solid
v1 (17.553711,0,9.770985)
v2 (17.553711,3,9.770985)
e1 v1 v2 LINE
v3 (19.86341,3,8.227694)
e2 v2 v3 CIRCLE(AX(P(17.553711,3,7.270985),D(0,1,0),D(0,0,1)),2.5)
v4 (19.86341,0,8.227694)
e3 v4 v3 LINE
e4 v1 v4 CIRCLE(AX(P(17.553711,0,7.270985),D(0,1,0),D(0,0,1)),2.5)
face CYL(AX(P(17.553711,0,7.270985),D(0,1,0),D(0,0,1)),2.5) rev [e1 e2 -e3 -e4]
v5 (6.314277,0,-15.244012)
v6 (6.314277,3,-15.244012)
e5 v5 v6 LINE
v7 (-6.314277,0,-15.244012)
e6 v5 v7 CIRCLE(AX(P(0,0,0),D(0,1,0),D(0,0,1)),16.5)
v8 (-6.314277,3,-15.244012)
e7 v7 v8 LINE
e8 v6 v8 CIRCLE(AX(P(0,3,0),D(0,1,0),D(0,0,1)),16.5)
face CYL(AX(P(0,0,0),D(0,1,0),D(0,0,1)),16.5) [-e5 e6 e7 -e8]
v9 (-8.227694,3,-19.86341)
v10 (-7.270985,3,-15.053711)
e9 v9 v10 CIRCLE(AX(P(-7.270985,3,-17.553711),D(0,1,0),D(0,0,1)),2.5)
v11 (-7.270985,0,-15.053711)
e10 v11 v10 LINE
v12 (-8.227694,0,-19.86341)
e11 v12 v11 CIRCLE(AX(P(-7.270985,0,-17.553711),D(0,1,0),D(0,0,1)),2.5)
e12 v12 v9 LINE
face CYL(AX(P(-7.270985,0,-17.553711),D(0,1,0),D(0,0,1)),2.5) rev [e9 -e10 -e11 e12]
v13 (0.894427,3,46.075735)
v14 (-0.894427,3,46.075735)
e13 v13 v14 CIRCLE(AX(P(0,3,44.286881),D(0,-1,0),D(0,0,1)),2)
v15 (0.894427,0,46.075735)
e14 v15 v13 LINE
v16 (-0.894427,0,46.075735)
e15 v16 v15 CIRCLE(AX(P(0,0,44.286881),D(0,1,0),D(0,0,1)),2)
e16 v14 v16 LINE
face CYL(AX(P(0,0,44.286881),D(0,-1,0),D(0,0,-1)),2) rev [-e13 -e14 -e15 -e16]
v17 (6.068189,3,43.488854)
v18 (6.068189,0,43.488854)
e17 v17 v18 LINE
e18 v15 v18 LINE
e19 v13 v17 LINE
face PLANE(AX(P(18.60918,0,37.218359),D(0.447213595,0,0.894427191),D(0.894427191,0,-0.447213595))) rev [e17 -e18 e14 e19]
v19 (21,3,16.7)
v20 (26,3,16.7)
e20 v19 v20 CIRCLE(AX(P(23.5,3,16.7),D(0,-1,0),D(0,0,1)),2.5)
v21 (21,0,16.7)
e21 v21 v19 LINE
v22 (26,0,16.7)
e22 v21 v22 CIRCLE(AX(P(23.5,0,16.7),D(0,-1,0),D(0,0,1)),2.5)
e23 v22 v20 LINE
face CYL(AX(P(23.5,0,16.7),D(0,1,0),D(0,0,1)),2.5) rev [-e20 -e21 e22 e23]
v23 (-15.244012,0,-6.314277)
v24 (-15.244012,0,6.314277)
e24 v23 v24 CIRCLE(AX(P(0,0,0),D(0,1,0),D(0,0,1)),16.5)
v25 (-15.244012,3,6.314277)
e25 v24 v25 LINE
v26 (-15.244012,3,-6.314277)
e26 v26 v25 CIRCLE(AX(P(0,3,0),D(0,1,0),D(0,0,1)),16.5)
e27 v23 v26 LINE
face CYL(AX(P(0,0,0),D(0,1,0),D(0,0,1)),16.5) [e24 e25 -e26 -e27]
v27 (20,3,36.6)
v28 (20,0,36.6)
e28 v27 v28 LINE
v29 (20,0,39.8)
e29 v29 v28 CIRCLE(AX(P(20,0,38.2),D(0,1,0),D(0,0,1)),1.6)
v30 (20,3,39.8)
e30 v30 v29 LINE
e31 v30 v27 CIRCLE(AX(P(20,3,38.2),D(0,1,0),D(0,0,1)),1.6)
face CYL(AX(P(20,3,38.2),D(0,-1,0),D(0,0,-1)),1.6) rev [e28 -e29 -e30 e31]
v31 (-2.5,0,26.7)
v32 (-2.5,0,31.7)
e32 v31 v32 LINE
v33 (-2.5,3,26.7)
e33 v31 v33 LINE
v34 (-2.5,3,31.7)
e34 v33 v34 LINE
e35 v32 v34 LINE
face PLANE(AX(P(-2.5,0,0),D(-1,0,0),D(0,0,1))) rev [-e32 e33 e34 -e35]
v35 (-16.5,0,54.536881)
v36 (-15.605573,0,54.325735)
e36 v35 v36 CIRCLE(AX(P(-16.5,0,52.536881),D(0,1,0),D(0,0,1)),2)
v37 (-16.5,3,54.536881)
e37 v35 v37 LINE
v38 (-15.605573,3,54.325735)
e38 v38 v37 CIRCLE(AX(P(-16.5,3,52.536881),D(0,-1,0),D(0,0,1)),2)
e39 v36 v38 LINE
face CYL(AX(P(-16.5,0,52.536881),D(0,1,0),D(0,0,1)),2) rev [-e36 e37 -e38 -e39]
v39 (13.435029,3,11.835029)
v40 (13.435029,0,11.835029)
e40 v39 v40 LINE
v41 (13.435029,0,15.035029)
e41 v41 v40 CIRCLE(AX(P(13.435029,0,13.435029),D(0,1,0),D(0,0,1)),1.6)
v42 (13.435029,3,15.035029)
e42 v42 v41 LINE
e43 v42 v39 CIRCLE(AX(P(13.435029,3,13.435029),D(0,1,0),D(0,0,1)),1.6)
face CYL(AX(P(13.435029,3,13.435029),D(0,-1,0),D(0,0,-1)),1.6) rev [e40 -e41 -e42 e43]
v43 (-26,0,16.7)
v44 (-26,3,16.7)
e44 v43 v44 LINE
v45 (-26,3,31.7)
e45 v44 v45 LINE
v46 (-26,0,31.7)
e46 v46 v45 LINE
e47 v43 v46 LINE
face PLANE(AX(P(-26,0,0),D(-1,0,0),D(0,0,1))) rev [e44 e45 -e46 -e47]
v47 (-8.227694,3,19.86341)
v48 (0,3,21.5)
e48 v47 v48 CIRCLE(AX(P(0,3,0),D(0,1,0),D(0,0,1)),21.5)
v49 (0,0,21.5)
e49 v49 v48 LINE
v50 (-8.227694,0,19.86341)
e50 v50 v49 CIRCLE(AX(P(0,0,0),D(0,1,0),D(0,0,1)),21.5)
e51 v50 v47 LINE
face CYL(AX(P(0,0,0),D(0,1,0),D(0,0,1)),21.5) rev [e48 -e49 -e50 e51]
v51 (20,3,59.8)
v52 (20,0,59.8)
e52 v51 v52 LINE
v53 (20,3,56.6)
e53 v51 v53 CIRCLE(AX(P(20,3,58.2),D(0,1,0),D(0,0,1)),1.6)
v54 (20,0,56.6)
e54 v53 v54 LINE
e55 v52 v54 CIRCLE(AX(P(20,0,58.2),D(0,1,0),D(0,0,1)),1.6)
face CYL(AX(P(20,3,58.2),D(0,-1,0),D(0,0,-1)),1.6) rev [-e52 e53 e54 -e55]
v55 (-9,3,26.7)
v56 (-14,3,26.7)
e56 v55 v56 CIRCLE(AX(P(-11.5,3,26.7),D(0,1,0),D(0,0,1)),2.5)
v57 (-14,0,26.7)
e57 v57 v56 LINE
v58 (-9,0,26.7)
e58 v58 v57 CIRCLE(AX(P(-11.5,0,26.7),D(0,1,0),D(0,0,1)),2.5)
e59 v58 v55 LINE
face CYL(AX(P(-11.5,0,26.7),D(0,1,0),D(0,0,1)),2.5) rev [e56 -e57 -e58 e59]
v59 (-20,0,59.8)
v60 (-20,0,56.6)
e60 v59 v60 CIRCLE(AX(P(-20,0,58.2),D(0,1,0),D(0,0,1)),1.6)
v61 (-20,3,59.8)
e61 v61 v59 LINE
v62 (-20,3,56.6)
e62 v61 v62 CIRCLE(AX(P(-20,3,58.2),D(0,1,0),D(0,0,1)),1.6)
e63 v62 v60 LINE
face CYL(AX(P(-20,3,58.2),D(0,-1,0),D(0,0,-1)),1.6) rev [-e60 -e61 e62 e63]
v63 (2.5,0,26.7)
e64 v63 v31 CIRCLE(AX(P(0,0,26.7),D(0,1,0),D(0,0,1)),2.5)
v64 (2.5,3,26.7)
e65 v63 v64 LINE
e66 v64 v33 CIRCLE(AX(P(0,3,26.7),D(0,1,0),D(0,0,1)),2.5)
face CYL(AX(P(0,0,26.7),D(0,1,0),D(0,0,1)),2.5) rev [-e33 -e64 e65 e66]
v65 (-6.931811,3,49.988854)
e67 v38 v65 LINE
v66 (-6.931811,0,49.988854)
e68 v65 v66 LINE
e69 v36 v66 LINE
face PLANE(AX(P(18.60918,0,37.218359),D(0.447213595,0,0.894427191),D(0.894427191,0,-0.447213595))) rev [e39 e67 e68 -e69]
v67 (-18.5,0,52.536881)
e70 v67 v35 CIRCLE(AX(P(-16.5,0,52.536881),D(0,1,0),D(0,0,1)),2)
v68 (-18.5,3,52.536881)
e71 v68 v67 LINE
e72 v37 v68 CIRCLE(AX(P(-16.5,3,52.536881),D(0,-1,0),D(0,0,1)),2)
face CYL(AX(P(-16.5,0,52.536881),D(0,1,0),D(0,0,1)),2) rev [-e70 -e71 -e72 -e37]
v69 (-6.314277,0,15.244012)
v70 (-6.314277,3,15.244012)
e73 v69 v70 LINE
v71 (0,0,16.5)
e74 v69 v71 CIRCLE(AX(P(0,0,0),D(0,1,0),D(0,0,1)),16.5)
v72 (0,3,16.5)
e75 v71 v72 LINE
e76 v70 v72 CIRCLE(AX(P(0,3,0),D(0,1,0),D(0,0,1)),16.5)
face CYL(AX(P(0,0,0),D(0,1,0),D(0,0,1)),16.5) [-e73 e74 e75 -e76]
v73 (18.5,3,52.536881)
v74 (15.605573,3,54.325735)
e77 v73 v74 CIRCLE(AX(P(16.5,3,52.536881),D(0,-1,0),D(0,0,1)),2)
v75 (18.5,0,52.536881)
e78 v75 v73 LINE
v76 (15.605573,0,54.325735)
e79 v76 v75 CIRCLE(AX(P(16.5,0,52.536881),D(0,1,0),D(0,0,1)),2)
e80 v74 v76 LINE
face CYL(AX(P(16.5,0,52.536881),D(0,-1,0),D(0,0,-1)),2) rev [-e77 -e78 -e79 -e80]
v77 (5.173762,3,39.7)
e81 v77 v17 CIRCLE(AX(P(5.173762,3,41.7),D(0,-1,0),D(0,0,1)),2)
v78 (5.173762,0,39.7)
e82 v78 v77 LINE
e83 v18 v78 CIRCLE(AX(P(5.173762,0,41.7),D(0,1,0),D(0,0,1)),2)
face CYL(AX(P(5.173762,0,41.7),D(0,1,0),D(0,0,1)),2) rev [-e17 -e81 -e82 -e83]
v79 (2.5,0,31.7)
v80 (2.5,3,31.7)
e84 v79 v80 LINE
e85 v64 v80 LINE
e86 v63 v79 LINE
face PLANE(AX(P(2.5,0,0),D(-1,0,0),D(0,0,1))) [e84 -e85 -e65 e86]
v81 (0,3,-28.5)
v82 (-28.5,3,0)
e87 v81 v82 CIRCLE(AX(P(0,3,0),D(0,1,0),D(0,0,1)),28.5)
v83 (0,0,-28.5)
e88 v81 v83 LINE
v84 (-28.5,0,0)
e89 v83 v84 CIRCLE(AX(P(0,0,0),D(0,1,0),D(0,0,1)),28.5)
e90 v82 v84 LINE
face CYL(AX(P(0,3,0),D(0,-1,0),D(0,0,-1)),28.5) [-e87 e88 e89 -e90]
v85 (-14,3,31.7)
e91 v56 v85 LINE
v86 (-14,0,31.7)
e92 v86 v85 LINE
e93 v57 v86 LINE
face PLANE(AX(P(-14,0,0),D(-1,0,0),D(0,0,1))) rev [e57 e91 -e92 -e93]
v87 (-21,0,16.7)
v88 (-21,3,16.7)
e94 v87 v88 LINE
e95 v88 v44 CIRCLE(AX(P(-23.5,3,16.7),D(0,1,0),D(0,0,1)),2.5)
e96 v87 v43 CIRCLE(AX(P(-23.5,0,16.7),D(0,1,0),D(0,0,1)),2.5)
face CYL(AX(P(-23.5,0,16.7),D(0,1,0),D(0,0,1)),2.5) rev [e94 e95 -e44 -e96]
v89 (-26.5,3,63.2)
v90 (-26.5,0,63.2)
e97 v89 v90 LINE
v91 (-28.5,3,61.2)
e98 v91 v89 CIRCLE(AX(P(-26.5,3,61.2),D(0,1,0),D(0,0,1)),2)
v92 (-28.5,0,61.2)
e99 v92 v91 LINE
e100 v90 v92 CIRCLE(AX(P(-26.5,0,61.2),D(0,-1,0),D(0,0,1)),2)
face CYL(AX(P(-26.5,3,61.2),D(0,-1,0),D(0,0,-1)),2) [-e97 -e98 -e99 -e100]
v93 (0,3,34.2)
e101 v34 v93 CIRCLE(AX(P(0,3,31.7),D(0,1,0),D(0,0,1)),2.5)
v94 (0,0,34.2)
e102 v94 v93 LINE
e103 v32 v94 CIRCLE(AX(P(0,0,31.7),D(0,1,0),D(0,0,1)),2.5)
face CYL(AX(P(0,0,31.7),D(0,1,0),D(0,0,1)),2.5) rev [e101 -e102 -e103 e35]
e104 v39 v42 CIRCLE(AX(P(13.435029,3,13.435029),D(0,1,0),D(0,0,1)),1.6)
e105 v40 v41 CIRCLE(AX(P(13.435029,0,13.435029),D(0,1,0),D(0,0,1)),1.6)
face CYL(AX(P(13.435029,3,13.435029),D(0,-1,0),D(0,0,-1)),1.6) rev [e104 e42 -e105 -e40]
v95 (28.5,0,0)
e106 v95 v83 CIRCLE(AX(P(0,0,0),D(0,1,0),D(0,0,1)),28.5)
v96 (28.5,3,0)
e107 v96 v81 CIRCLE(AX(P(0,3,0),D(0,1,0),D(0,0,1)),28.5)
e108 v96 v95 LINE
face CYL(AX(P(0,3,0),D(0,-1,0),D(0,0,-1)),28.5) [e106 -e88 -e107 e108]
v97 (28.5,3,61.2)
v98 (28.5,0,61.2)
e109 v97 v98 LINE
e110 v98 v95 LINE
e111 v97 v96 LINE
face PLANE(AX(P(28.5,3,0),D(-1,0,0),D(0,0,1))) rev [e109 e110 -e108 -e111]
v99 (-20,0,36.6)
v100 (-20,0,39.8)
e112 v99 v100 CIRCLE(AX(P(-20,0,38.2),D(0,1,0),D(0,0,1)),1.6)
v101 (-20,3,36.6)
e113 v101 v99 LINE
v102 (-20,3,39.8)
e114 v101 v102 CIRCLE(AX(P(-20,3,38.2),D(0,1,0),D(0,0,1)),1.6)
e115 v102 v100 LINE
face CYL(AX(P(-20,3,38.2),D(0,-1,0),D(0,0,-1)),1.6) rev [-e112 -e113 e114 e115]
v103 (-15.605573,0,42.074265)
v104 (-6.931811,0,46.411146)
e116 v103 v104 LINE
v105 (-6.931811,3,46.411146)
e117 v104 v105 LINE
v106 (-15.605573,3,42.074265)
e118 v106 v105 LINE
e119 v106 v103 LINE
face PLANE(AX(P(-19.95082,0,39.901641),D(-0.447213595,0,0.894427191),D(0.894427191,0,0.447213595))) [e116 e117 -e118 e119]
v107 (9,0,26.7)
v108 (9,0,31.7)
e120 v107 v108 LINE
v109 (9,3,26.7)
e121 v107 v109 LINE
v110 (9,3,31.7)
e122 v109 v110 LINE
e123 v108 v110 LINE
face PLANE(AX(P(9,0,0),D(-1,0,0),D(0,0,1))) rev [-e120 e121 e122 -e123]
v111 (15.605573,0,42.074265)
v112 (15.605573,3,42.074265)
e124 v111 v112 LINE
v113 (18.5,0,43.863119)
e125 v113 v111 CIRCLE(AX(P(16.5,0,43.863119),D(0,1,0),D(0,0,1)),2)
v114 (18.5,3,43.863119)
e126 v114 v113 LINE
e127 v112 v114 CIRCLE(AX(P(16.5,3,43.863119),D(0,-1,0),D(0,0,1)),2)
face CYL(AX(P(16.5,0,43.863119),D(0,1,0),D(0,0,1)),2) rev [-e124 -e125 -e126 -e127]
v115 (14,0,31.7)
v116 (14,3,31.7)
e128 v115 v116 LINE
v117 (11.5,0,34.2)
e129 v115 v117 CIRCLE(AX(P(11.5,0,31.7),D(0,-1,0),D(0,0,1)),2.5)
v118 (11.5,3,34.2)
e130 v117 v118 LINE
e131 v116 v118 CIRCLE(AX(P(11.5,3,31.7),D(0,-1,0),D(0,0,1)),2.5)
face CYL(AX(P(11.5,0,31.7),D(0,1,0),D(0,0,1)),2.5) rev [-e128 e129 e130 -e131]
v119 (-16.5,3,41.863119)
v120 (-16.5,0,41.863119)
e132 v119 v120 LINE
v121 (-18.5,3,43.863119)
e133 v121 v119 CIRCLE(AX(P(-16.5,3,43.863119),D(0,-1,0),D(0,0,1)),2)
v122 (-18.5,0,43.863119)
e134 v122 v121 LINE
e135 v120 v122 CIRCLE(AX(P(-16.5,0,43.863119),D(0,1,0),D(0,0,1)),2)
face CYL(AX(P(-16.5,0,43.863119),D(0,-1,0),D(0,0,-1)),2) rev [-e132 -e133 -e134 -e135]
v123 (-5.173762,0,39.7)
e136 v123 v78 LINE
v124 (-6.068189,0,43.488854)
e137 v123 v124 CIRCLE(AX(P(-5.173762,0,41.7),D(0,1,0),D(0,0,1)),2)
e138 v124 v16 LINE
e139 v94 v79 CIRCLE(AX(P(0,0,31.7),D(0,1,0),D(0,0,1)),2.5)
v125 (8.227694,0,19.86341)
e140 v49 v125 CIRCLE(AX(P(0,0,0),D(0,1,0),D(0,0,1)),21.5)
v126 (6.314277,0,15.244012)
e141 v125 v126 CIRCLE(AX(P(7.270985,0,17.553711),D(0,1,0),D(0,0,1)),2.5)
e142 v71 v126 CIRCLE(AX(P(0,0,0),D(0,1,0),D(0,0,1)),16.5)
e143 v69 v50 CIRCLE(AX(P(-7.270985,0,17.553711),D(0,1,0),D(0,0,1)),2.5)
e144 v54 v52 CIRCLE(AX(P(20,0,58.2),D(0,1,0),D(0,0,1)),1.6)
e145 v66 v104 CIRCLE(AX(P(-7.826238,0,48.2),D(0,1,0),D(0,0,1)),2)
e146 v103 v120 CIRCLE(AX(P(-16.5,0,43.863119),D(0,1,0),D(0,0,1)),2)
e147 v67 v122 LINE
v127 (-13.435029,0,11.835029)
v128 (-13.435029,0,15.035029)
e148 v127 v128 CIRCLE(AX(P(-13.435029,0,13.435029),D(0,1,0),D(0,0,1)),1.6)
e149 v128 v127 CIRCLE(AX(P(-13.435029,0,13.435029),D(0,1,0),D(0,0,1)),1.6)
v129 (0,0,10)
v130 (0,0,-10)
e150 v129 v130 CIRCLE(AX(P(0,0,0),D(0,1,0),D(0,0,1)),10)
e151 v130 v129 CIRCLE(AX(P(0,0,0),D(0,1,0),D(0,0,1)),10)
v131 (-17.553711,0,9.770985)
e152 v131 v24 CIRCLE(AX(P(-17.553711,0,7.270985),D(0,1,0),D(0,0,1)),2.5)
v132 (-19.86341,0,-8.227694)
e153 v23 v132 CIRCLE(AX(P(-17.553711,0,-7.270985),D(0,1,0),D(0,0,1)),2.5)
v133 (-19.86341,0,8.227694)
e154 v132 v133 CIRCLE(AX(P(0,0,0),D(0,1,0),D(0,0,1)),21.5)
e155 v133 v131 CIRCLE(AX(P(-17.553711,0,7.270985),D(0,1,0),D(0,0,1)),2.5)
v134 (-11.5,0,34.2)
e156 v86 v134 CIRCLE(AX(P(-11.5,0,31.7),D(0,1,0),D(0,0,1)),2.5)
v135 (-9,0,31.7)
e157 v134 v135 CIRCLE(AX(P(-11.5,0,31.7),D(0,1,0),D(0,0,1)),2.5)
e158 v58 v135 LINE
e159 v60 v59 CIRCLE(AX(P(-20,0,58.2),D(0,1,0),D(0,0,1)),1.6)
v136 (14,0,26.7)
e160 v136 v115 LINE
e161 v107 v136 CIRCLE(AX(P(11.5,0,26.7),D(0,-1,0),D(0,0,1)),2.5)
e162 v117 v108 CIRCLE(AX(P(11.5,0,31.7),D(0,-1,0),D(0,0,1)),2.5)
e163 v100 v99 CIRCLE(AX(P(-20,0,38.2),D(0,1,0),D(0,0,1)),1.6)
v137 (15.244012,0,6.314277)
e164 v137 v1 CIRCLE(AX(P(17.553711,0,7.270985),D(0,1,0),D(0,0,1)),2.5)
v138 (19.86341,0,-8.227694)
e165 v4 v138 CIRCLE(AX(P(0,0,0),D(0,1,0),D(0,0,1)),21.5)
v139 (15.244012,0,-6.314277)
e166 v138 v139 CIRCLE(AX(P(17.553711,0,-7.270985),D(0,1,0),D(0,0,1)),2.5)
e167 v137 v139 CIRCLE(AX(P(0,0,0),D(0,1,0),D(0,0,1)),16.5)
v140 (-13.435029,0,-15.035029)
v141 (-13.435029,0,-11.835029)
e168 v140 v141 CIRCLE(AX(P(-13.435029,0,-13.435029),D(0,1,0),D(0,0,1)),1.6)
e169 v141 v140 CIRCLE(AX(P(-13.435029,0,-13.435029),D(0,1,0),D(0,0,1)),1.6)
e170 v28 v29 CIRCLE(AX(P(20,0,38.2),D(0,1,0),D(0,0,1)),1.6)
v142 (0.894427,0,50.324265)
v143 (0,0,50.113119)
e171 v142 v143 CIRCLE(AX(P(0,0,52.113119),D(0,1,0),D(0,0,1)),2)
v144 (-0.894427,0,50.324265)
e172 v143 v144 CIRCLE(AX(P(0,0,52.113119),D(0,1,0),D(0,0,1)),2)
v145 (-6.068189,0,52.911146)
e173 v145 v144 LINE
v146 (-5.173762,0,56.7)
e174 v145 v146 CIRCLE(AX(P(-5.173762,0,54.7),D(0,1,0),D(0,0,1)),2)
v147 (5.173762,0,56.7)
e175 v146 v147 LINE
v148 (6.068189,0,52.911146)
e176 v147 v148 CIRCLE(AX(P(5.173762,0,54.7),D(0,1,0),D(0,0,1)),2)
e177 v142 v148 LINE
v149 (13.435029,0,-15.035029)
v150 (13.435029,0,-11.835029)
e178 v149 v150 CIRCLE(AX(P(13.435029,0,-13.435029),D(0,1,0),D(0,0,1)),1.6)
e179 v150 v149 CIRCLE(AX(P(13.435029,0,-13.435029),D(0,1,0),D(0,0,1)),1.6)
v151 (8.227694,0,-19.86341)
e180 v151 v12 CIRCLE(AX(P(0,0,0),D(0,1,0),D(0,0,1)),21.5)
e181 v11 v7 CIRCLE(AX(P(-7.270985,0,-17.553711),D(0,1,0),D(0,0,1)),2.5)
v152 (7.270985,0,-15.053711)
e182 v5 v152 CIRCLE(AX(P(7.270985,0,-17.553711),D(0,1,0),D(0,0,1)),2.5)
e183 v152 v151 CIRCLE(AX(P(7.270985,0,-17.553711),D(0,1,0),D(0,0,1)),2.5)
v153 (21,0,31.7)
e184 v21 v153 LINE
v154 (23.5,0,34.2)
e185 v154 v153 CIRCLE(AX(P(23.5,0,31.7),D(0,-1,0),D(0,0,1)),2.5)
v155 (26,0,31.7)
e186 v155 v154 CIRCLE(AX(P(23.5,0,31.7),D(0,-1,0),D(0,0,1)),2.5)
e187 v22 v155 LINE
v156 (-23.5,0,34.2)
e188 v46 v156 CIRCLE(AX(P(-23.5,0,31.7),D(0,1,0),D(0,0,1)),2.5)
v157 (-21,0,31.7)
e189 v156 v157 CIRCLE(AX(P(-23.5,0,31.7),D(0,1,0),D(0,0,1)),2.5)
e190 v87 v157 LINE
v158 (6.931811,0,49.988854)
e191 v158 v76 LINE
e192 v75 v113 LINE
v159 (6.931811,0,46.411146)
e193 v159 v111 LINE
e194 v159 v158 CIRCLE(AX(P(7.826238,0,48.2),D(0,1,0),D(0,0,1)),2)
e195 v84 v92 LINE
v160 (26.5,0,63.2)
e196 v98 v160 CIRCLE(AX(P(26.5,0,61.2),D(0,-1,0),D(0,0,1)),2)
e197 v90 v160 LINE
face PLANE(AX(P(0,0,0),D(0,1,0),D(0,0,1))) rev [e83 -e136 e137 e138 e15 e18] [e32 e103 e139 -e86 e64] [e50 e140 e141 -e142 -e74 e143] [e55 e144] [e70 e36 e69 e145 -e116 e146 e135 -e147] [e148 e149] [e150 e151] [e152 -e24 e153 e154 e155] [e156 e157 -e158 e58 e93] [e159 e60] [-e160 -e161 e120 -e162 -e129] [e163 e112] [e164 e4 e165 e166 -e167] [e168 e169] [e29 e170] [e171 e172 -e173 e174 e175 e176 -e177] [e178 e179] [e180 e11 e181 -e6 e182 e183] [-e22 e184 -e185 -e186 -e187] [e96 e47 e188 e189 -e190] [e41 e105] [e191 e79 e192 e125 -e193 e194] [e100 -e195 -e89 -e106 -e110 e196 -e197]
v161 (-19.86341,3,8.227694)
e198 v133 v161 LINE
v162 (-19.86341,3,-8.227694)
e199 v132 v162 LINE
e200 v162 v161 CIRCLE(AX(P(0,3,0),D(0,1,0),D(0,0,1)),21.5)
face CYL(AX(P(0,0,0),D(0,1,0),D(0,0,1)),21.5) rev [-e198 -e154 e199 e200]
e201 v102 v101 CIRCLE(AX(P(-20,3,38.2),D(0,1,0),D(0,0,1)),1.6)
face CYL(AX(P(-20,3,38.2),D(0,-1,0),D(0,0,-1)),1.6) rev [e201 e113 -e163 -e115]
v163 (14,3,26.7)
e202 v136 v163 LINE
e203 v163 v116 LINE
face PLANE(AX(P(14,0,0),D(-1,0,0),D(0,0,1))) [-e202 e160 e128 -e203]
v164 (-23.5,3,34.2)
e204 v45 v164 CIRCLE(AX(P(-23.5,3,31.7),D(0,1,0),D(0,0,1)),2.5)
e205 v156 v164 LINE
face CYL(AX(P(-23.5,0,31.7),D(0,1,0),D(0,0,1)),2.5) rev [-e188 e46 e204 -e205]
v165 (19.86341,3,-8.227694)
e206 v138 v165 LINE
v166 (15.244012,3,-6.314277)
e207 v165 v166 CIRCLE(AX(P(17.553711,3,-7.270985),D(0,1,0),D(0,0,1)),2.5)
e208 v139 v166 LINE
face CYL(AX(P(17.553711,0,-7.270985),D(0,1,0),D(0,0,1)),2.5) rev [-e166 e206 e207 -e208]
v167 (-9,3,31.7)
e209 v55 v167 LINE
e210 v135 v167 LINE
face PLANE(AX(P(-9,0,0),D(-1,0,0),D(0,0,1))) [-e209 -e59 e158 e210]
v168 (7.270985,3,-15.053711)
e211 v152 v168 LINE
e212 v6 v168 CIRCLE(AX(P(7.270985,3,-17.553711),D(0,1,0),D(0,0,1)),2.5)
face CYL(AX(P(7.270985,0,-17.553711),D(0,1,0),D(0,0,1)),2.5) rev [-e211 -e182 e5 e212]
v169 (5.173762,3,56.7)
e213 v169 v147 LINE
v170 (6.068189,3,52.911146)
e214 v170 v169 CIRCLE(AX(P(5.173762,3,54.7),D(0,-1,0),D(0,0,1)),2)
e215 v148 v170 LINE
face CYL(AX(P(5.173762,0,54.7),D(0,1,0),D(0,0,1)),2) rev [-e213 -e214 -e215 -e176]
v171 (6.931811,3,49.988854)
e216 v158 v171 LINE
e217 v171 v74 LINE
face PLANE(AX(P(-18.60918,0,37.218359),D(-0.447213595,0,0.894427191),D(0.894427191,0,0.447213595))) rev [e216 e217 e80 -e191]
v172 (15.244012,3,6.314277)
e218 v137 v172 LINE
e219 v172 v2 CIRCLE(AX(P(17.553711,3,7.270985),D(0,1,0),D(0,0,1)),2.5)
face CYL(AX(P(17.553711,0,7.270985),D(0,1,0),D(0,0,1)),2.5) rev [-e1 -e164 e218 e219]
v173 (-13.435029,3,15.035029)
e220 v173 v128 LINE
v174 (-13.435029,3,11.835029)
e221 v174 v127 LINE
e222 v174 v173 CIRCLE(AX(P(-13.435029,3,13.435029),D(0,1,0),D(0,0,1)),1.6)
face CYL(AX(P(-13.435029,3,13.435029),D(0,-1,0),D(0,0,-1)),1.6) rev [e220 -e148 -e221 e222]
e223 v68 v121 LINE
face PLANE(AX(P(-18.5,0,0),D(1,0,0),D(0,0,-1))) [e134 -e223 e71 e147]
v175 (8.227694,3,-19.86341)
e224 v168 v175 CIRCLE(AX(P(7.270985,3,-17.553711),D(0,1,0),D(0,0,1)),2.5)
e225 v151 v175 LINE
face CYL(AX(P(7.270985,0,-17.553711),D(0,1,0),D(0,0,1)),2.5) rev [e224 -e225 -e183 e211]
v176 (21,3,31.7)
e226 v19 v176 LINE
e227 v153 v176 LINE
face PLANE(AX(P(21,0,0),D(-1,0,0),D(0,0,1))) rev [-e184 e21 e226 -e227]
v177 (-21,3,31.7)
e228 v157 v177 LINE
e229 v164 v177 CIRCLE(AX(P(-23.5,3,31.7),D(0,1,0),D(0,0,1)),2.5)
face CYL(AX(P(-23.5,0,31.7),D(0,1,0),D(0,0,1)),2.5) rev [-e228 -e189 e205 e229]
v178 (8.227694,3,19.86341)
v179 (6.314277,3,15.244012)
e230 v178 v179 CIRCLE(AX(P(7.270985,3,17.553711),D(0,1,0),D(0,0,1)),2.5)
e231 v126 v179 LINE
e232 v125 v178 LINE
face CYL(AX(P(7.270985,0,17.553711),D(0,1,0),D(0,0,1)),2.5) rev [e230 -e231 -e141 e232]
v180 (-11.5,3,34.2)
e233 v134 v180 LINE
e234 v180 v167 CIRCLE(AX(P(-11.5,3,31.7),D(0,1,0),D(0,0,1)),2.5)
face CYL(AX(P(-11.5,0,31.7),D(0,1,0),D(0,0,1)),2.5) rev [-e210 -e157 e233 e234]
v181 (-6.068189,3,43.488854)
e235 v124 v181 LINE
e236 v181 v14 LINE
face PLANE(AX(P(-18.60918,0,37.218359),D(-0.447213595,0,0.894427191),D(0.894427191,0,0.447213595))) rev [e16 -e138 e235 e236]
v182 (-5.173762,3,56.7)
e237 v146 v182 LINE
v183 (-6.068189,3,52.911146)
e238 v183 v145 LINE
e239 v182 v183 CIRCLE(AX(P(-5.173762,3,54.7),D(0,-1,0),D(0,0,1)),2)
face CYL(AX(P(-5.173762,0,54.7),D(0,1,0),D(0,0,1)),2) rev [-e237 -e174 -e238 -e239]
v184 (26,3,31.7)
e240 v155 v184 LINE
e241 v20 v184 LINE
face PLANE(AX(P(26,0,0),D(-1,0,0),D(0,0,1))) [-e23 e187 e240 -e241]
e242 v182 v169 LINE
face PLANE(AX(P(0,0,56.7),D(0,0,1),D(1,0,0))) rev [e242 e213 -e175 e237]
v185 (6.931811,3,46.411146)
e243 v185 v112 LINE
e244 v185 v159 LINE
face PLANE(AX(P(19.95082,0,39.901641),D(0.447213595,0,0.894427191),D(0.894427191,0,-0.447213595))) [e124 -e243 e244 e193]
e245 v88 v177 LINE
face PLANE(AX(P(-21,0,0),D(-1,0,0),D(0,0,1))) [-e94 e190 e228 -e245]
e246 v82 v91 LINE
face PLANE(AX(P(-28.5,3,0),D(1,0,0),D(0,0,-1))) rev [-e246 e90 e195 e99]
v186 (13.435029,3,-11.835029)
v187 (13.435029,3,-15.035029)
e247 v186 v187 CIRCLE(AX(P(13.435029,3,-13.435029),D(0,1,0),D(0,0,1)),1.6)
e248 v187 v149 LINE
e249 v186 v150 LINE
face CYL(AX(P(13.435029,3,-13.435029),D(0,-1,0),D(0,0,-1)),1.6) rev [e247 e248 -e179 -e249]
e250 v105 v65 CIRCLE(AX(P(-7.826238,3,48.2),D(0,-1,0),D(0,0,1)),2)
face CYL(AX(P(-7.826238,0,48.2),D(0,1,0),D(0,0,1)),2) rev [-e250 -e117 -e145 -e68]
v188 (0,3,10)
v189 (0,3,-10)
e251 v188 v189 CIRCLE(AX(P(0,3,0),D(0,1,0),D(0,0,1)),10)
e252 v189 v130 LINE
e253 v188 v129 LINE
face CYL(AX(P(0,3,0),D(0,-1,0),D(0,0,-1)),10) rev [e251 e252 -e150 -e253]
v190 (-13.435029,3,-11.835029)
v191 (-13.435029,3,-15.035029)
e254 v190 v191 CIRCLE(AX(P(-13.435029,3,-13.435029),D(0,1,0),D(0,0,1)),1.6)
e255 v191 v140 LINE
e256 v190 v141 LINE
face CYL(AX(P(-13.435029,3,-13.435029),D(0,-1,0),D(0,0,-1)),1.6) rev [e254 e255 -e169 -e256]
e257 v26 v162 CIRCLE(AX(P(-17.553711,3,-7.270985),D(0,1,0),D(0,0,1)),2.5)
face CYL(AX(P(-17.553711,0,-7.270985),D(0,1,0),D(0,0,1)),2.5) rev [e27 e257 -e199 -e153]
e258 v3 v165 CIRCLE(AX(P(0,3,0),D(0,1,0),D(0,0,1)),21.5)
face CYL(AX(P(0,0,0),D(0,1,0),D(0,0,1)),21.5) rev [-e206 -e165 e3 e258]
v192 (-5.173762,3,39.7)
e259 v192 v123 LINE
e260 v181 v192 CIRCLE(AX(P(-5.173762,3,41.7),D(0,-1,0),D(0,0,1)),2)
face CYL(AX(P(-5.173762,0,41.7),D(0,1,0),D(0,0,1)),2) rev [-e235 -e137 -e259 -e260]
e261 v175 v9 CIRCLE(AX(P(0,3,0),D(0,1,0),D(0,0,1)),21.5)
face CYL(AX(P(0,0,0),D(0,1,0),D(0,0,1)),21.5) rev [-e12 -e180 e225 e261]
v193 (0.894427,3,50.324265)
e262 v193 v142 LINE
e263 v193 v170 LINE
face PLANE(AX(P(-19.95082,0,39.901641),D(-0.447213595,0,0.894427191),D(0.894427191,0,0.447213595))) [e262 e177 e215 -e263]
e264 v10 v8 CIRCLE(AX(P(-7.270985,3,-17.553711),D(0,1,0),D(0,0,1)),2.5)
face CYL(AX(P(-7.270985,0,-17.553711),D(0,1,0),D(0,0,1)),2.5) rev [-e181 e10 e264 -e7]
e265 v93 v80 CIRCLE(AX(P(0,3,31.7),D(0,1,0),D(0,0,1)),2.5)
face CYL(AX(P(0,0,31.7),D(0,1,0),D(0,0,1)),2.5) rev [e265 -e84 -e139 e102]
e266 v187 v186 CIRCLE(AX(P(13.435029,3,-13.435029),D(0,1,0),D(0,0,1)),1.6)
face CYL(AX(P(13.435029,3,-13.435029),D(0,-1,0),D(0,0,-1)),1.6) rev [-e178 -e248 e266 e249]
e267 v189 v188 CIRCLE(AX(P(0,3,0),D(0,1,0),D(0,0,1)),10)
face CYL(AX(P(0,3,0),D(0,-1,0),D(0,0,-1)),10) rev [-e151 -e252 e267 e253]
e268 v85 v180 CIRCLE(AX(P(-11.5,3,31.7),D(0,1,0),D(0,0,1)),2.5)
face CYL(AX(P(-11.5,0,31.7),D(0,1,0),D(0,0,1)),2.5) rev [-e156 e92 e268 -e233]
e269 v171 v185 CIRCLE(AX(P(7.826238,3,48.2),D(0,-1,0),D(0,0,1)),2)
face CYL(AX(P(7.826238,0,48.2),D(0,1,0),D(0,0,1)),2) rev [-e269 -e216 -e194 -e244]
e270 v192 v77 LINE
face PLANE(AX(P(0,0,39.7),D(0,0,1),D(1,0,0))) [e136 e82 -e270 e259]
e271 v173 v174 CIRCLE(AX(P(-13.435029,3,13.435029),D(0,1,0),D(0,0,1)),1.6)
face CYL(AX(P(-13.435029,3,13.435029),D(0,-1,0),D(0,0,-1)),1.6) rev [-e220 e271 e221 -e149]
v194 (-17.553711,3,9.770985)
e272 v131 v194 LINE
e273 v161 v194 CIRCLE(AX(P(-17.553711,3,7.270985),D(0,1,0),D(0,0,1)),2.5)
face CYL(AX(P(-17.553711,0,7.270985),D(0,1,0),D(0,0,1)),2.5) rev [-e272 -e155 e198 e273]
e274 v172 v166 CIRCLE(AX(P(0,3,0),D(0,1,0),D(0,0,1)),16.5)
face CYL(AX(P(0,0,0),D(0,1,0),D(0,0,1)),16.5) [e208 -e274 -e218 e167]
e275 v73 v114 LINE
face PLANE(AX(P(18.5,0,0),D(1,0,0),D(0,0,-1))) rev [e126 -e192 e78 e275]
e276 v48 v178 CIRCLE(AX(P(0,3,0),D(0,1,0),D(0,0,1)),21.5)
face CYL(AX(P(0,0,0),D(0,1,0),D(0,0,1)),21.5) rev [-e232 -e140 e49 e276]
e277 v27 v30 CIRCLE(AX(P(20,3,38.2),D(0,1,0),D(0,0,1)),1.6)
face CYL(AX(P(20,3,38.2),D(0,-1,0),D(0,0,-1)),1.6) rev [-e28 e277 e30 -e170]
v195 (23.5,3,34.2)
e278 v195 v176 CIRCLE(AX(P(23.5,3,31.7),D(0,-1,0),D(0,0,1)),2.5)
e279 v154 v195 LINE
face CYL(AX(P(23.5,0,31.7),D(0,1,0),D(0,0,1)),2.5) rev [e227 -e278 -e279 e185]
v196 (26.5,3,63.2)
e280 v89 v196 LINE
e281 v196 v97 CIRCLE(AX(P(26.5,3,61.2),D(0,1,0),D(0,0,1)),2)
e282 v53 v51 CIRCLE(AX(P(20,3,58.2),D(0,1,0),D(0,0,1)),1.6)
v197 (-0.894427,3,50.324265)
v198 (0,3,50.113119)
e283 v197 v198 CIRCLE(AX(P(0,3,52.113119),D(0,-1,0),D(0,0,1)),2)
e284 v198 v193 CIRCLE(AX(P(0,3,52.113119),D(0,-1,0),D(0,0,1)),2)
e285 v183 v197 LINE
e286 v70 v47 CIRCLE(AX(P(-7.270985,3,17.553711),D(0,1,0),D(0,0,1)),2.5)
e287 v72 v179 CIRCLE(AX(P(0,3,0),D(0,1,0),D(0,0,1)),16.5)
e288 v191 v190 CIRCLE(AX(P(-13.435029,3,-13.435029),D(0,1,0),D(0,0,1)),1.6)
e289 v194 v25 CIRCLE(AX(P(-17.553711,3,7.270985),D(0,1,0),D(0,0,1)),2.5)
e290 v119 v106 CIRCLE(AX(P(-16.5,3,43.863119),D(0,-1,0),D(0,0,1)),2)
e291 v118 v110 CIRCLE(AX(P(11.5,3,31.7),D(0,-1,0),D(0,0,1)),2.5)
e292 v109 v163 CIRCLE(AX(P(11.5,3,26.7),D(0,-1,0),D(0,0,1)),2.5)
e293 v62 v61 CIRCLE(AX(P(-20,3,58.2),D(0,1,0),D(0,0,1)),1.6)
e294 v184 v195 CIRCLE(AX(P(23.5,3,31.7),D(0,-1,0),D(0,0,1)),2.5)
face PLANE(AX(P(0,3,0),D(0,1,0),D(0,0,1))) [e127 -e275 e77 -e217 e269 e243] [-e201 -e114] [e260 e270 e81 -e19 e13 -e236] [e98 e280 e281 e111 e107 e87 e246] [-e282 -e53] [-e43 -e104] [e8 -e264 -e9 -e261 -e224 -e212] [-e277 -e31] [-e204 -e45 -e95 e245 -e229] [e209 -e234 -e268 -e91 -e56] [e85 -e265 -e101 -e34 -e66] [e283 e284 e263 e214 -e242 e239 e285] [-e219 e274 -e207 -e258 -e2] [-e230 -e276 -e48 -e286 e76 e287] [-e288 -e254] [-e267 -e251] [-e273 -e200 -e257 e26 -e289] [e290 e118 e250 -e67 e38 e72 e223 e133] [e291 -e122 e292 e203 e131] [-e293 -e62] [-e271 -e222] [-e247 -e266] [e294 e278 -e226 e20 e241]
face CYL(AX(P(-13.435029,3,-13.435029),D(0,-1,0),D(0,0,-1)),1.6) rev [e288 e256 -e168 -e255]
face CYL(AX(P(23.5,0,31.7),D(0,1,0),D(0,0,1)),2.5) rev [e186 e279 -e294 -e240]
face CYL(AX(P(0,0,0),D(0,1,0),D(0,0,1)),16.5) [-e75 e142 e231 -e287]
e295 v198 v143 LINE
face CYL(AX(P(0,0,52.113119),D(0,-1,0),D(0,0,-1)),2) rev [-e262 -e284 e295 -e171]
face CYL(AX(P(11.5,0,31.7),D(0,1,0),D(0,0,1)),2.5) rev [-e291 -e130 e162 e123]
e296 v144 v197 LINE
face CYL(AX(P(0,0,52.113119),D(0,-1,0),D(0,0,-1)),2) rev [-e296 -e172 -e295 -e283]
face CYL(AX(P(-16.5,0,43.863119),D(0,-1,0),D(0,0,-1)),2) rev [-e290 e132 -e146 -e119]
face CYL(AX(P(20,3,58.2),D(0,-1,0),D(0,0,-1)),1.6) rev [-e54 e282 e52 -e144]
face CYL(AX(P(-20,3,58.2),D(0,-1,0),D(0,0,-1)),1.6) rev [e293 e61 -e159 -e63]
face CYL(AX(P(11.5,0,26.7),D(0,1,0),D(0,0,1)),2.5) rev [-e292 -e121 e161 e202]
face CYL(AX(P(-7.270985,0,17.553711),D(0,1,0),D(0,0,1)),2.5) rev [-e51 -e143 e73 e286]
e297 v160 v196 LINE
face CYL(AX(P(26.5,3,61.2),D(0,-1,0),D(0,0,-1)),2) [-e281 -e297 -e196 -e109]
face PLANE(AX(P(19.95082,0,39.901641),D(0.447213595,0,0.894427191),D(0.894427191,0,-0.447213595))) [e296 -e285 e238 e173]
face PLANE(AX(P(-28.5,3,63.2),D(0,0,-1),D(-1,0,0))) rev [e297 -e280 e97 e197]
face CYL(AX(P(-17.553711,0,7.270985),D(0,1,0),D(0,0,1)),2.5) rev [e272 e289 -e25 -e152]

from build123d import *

# Parameters (mm, degrees)
SKETCH_1_R          = 1.6
SKETCH_1_R_2        = 10
EXTRUDE_1_DEPTH     = 3
CUT_EXTRUDE_1_DEPTH = 3
FILLET_1_R          = 2


with BuildPart() as part:
    # 草图1 → 凸台-拉伸1 (new body)
    with BuildSketch(Plane(origin=(0, 0, 0), x_dir=(1, 0, 0), z_dir=(0, 1, 0))):
        with BuildLine():
            Line((-28.5, 0), (-28.5, -63.2))
            Line((-28.5, -63.2), (28.5, -63.2))
            Line((28.5, -63.2), (28.5, 0))
            ThreePointArc((28.5, 0), (0, 28.5), (-28.5, 0))
        make_face()
        with Locations(Location((-20, -38.2, 0), (0, 0, 270))):
            Circle(SKETCH_1_R, mode=Mode.SUBTRACT)
        with Locations(Location((20, -38.2, 0), (0, 0, 270))):
            Circle(SKETCH_1_R, mode=Mode.SUBTRACT)
        with Locations(Location((20, -58.2, 0), (0, 0, 270))):
            Circle(SKETCH_1_R, mode=Mode.SUBTRACT)
        with Locations(Location((-20, -58.2, 0), (0, 0, 270))):
            Circle(SKETCH_1_R, mode=Mode.SUBTRACT)
        with Locations(Location((0, 0, 0), (0, 0, 270))):
            Circle(SKETCH_1_R_2, mode=Mode.SUBTRACT)
        with Locations(Location((-13.435028843, 13.435028843, 0), (0, 0, 270))):
            Circle(SKETCH_1_R, mode=Mode.SUBTRACT)
        with Locations(Location((13.435028843, 13.435028843, 0), (0, 0, 270))):
            Circle(SKETCH_1_R, mode=Mode.SUBTRACT)
        with Locations(Location((13.435028843, -13.435028843, 0), (0, 0, 270))):
            Circle(SKETCH_1_R, mode=Mode.SUBTRACT)
        with Locations(Location((-13.435028843, -13.435028843, 0), (0, 0, 270))):
            Circle(SKETCH_1_R, mode=Mode.SUBTRACT)
    extrude(amount=EXTRUDE_1_DEPTH)

    # 草图2 → 切除-拉伸1 (cut)
    with BuildSketch(Plane(origin=(0, 3, 0), x_dir=(1, 0, 0), z_dir=(0, 1, 0))):
        Polygon((-18.5, -40.627050983), (-18.5, -55.772949017), (-3.354101966, -48.2), align=None)
        Polygon((13.645898034, -39.7), (-13.645898034, -39.7), (0, -46.522949017), align=None)
        Polygon((3.354101966, -48.2), (18.5, -55.772949017), (18.5, -40.627050983), align=None)
        Polygon((0, -49.877050983), (-13.645898034, -56.7), (13.645898034, -56.7), align=None)
        with BuildLine():
            Line((-2.5, -26.7), (-2.5, -31.7))
            ThreePointArc((-2.5, -31.7), (0, -34.2), (2.5, -31.7))
            Line((2.5, -31.7), (2.5, -26.7))
            ThreePointArc((2.5, -26.7), (0, -24.2), (-2.5, -26.7))
        make_face()
        with BuildLine():
            ThreePointArc((14, -31.7), (11.5, -34.2), (9, -31.7))
            Line((9, -31.7), (9, -26.7))
            ThreePointArc((9, -26.7), (11.5, -24.2), (14, -26.7))
            Line((14, -26.7), (14, -31.7))
        make_face()
        with BuildLine():
            ThreePointArc((26, -31.7), (23.5, -34.2), (21, -31.7))
            Line((21, -31.7), (21, -16.7))
            ThreePointArc((21, -16.7), (23.5, -14.2), (26, -16.7))
            Line((26, -16.7), (26, -31.7))
        make_face()
        with BuildLine():
            ThreePointArc((-8.227693796, -19.863409949), (0, -21.5), (8.227693796, -19.863409949))
            ThreePointArc((8.227693796, -19.863409949), (9.580684046, -16.597002537), (6.314276634, -15.244012286))
            ThreePointArc((6.314276634, -15.244012286), (0, -16.5), (-6.314276634, -15.244012286))
            ThreePointArc((-6.314276634, -15.244012286), (-9.580684046, -16.597002537), (-8.227693796, -19.863409949))
        make_face()
        with BuildLine():
            Line((-14, -26.7), (-14, -31.7))
            ThreePointArc((-14, -31.7), (-11.5, -34.2), (-9, -31.7))
            Line((-9, -31.7), (-9, -26.7))
            ThreePointArc((-9, -26.7), (-11.5, -24.2), (-14, -26.7))
        make_face()
        with BuildLine():
            Line((-26, -16.7), (-26, -31.7))
            ThreePointArc((-26, -31.7), (-23.5, -34.2), (-21, -31.7))
            Line((-21, -31.7), (-21, -16.7))
            ThreePointArc((-21, -16.7), (-23.5, -14.2), (-26, -16.7))
        make_face()
        with BuildLine():
            ThreePointArc((-19.863409949, 8.227693796), (-21.5, 0), (-19.863409949, -8.227693796))
            ThreePointArc((-19.863409949, -8.227693796), (-16.597002537, -9.580684046), (-15.244012286, -6.314276634))
            ThreePointArc((-15.244012286, -6.314276634), (-16.5, 0), (-15.244012286, 6.314276634))
            ThreePointArc((-15.244012286, 6.314276634), (-16.597002537, 9.580684046), (-19.863409949, 8.227693796))
        make_face()
        with BuildLine():
            ThreePointArc((19.863409949, -8.227693796), (21.5, 0), (19.863409949, 8.227693796))
            ThreePointArc((19.863409949, 8.227693796), (16.597002537, 9.580684046), (15.244012286, 6.314276634))
            ThreePointArc((15.244012286, 6.314276634), (16.5, 0), (15.244012286, -6.314276634))
            ThreePointArc((15.244012286, -6.314276634), (16.597002537, -9.580684046), (19.863409949, -8.227693796))
        make_face()
        with BuildLine():
            ThreePointArc((8.227693796, 19.863409949), (0, 21.5), (-8.227693796, 19.863409949))
            ThreePointArc((-8.227693796, 19.863409949), (-9.580684046, 16.597002537), (-6.314276634, 15.244012286))
            ThreePointArc((-6.314276634, 15.244012286), (0, 16.5), (6.314276634, 15.244012286))
            ThreePointArc((6.314276634, 15.244012286), (9.580684046, 16.597002537), (8.227693796, 19.863409949))
        make_face()
    extrude(amount=-CUT_EXTRUDE_1_DEPTH, mode=Mode.SUBTRACT)

    # 圆角1
    fillet_1_edges = [part.edges().sort_by_distance(p)[0] for p in [
        (3.354101966, 1.5, 48.2),
        (18.5, 1.5, 40.627050983),
        (18.5, 1.5, 55.772949017),
        (-13.645898034, 1.5, 39.7),
        (13.645898034, 1.5, 39.7),
        (0, 1.5, 46.522949017),
        (-13.645898034, 1.5, 56.7),
        (0, 1.5, 49.877050983),
        (13.645898034, 1.5, 56.7),
        (-18.5, 1.5, 55.772949017),
        (-18.5, 1.5, 40.627050983),
        (-3.354101966, 1.5, 48.2),
        (28.5, 1.5, 63.2),
        (-28.5, 1.5, 63.2),
    ]]
    fillet(fillet_1_edges, radius=FILLET_1_R)


solid = part.part
